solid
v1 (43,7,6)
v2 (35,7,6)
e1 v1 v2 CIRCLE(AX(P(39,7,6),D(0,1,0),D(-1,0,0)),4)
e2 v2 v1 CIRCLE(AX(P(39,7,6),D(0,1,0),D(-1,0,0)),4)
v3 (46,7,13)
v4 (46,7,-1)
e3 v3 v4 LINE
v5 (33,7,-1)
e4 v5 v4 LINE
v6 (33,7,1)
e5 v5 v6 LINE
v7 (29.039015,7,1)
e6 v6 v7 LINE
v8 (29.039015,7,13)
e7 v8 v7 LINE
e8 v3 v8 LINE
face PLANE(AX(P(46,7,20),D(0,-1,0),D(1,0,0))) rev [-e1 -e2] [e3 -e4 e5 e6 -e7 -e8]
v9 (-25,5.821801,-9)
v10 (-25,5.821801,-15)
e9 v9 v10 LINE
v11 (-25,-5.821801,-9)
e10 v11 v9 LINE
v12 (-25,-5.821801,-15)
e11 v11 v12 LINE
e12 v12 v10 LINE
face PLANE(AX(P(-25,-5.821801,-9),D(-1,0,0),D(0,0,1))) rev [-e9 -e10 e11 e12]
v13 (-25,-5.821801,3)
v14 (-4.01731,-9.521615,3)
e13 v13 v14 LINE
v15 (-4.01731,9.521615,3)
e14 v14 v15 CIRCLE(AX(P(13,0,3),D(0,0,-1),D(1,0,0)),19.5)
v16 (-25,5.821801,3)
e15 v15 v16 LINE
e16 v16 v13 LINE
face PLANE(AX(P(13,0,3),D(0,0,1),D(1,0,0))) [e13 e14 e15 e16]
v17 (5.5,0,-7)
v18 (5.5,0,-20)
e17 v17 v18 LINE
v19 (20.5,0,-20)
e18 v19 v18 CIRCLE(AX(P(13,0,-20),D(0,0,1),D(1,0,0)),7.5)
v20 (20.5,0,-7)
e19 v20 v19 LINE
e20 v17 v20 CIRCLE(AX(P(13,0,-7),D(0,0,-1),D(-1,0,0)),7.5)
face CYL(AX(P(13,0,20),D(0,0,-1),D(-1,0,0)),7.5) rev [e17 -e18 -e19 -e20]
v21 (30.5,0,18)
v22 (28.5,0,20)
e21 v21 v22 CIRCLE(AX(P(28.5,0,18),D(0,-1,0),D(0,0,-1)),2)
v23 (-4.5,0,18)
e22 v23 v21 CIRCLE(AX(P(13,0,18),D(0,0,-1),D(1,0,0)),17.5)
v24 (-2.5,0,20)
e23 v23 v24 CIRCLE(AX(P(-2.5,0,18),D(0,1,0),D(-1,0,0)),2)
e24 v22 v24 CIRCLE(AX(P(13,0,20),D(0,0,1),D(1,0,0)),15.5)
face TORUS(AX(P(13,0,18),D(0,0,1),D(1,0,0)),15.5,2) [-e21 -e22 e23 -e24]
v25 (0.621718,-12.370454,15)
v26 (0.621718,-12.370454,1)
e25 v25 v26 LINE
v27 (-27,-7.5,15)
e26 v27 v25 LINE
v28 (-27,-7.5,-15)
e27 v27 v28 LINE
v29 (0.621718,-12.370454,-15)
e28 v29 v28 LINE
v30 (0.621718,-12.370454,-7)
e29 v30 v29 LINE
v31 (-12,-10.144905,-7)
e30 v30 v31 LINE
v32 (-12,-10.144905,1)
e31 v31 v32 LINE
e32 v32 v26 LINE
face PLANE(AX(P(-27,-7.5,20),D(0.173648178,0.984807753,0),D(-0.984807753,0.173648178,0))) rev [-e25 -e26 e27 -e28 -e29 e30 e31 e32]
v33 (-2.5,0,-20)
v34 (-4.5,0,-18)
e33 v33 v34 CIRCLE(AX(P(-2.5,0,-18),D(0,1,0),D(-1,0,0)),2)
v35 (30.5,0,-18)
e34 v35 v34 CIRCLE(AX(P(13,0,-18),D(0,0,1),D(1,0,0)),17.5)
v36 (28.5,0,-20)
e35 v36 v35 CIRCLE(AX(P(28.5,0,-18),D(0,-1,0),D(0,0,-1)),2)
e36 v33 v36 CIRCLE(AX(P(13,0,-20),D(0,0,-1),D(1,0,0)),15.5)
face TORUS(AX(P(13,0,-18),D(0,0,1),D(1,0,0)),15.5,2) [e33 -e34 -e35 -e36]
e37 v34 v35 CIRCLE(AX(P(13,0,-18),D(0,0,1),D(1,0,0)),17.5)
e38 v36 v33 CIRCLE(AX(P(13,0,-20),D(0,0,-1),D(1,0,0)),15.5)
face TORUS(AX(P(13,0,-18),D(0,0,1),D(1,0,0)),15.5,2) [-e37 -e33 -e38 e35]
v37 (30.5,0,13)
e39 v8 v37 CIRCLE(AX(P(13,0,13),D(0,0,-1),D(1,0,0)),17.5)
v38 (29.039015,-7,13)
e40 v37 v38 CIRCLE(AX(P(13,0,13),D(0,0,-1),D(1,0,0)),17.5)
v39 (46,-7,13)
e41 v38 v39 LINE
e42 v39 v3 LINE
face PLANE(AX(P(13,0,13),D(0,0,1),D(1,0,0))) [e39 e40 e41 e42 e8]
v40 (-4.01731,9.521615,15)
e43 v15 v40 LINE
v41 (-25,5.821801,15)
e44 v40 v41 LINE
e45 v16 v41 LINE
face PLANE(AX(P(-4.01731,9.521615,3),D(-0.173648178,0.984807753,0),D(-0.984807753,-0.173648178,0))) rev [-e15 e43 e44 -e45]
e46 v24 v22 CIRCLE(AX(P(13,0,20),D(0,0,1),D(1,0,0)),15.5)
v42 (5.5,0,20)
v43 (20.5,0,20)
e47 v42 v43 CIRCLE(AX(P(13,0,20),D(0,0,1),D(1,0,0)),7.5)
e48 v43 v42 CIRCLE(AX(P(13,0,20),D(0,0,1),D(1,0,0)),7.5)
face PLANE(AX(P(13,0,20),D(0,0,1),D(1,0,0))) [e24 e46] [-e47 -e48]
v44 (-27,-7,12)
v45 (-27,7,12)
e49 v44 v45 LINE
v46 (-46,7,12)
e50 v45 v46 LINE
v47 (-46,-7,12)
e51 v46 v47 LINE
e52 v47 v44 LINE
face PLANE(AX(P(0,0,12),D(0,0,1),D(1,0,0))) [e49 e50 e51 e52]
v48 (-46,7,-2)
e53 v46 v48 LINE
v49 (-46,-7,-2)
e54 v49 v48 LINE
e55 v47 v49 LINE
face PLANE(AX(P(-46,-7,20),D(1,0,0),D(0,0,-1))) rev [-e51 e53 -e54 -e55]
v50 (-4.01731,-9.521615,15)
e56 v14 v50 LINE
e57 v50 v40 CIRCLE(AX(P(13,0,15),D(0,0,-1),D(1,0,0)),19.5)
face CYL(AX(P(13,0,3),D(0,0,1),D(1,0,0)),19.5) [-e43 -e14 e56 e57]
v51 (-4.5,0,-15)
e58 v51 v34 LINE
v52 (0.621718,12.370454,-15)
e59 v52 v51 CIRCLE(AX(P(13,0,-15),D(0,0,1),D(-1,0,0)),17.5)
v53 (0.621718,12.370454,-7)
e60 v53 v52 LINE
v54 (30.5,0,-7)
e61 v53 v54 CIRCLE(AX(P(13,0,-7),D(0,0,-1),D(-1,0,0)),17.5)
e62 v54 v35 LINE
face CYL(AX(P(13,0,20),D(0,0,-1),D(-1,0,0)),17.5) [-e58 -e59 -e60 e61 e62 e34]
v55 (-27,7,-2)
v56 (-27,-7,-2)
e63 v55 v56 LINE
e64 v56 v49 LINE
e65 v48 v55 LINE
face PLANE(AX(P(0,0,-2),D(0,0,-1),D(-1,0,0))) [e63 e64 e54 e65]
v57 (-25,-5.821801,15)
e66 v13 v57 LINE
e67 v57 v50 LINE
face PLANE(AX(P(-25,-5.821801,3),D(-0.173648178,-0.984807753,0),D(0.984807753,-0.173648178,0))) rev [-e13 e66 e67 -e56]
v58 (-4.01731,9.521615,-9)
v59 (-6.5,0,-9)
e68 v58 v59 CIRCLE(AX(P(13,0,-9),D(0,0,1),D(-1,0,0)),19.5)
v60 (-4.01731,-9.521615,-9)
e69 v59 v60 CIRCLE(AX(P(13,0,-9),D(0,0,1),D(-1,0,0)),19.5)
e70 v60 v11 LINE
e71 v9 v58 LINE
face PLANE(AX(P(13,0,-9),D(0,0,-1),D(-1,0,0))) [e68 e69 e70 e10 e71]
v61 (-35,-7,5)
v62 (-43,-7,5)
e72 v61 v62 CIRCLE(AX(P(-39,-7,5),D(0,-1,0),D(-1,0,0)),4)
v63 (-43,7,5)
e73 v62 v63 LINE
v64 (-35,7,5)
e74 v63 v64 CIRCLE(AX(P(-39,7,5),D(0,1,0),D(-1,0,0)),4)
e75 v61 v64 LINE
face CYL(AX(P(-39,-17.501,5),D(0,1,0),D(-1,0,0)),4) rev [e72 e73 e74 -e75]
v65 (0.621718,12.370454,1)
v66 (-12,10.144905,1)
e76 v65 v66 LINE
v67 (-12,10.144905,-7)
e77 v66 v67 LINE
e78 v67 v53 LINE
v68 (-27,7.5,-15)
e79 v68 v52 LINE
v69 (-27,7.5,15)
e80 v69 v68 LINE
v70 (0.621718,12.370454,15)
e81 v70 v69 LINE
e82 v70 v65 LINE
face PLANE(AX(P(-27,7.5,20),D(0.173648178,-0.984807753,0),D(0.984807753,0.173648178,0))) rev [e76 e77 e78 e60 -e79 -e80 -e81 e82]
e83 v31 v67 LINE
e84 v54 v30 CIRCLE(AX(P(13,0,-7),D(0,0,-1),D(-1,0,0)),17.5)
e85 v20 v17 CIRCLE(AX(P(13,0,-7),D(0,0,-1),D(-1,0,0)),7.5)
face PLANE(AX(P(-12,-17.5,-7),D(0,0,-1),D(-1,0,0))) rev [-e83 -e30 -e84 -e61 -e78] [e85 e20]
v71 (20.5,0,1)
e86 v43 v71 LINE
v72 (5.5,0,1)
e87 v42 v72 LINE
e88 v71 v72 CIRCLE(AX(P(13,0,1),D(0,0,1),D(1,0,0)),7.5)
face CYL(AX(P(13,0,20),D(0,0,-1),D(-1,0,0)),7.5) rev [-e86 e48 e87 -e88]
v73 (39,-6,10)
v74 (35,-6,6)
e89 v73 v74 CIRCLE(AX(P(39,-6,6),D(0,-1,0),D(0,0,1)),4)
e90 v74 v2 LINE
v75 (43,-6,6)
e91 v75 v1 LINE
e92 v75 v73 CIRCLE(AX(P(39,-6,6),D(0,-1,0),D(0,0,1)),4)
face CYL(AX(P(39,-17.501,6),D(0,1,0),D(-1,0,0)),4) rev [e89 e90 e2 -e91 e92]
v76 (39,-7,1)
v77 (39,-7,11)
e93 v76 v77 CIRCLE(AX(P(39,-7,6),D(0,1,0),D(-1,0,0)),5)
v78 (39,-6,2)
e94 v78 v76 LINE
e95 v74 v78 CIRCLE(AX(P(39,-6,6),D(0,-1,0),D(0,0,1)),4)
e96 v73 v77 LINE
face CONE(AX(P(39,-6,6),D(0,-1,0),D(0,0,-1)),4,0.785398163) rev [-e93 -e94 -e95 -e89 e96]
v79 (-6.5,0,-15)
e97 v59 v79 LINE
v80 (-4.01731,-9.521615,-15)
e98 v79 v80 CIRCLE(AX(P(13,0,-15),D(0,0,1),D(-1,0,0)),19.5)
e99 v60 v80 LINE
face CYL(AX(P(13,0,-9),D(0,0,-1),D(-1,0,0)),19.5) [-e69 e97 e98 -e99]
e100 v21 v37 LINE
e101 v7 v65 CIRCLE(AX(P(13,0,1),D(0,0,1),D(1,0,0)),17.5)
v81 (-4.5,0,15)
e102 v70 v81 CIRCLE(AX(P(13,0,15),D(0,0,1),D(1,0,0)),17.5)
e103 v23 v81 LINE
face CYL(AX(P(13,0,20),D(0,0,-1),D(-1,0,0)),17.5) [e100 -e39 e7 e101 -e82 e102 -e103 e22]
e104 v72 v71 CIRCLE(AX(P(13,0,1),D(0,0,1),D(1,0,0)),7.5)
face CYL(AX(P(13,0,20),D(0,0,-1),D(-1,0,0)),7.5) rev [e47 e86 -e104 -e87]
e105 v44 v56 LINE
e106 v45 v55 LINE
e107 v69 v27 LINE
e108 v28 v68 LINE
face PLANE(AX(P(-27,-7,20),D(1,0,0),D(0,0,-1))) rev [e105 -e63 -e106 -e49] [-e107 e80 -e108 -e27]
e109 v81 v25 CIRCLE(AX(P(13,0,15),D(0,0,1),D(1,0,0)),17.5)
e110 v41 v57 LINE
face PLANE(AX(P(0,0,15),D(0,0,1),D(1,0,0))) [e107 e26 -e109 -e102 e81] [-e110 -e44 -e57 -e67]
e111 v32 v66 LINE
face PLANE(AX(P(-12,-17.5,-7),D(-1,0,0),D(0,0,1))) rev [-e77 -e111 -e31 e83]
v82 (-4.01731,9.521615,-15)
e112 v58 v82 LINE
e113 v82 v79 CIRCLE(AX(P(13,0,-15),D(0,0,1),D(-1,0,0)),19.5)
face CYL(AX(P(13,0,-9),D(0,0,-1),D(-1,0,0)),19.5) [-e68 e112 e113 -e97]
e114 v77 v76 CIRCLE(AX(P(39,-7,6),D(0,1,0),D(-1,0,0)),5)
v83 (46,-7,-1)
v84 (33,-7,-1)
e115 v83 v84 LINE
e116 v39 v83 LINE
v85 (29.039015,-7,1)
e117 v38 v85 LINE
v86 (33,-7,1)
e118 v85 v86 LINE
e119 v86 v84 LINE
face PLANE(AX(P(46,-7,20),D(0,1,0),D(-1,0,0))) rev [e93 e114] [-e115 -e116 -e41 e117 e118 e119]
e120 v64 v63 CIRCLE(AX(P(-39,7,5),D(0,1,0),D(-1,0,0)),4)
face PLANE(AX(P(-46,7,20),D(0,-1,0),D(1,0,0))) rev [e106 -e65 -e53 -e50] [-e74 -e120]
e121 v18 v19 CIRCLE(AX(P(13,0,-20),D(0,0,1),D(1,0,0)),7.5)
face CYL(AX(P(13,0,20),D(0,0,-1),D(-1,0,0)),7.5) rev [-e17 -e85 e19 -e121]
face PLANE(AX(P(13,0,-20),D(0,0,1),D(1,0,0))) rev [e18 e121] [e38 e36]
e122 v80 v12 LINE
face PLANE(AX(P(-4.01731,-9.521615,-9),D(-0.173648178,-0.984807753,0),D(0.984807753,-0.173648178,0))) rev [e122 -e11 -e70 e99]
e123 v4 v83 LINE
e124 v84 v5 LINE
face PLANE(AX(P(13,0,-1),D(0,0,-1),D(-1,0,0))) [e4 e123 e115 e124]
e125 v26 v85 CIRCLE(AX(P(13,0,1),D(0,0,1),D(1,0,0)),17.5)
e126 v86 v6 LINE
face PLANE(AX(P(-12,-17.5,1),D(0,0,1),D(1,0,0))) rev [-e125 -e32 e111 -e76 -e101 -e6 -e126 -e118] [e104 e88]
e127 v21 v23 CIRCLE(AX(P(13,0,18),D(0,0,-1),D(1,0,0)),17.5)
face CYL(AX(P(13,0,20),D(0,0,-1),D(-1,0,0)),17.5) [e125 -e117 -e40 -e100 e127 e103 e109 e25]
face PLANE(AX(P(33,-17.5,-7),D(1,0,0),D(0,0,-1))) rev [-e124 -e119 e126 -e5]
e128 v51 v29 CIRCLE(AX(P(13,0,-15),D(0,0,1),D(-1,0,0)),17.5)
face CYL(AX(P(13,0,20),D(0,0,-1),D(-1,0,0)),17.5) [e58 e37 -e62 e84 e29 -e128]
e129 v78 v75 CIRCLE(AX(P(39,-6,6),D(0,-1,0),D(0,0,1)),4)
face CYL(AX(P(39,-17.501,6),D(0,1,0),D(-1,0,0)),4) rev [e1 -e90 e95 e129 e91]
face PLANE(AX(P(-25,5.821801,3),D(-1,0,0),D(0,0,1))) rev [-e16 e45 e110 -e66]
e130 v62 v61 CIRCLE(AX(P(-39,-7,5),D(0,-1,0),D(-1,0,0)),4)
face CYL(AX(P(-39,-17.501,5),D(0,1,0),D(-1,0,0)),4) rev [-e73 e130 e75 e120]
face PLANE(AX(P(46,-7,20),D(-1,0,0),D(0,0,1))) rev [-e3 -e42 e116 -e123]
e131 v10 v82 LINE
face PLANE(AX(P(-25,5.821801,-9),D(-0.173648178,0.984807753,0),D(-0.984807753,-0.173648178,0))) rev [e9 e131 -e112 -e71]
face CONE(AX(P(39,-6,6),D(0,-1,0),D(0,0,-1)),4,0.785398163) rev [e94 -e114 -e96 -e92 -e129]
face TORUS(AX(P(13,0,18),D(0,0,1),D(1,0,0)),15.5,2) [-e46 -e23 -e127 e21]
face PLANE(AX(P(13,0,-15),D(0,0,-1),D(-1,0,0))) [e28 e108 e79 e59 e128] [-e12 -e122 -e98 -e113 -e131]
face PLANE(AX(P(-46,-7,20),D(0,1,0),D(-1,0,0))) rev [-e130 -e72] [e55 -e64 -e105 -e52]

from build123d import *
from build123d.topology import SkipClean

# Parameters (mm, degrees)
BRACKET_SIDE_PROFILE_SKETCH_R = 7.5
BRACKET_BODY_40MM_DEPTH       = 20
TOP_SLOT_CUT_15X19_DEPTH      = 54.124852941
TOP_SLOT_CUT_15X19_DEPTH_BACK = 54.124852941
TOP_SLOT_SKETCH_W             = 45
TOP_SLOT_SKETCH_H             = 8
SIDE_RELIEF_A_CUT_7MM_DEPTH   = 7
SIDE_RELIEF_B_SKETCH_W        = 19
SIDE_RELIEF_B_SKETCH_H        = 14
SIDE_RELIEF_B_CUT_7MM_DEPTH   = 7
LUG_TRIM_A_CUT_5MM_DEPTH      = 5
LUG_START                     = -5
LUG_TRIM_B_CUT_5MM_DEPTH      = 5
HUB_GAP_SKETCH_W              = 19
HUB_GAP_SKETCH_H              = 14
HUB_GAP_CUT_18MM_DEPTH        = 18
RELIEF_STEP_SKETCH_W          = 19
RELIEF_STEP_SKETCH_H          = 14
RELIEF_STEP_CUT_1MM_DEPTH     = 1
WINDOW_START                  = -19
WINDOW_OPENING_CUT_19MM_DEPTH = 19
LUG_HOLE_A_CUT_12MM_DEPTH     = 12
LUG_START_2                   = -6
LUG_HOLE_B_CUT_6MM_DEPTH      = 6
EDGE_FILLET_R2_R              = 2
HUB_BORE_CUT_REACH            = 57.823
HUB_BORE_SKETCH_R             = 4
BORE_CHAMFER_1X45_SIZE        = 1


with BuildPart() as part:
    # Bracket Side Profile Sketch → Bracket Body 40mm (new, symmetric)
    with BuildSketch(Plane.XY):
        with BuildLine():
            Line((-46, -7), (-46, 7))
            Line((-46, 7), (-27, 7))
            Line((-27, 7), (-27, 7.5))
            Line((-27, 7.5), (0.62171804, 12.370454144))
            ThreePointArc((0.62171804, 12.370454144), (16.249720896, 17.195619038), (29.039014932, 7))
            Line((29.039014932, 7), (46, 7))
            Line((46, 7), (46, -7))
            Line((46, -7), (29.039014932, -7))
            ThreePointArc((29.039014932, -7), (16.249720896, -17.195619038), (0.62171804, -12.370454144))
            Line((0.62171804, -12.370454144), (-27, -7.5))
            Line((-27, -7.5), (-27, -7))
            Line((-27, -7), (-46, -7))
        make_face()
        with Locations((13, 0)):
            Circle(BRACKET_SIDE_PROFILE_SKETCH_R, mode=Mode.SUBTRACT)
    extrude(amount=BRACKET_BODY_40MM_DEPTH, both=True)

    # Top Slot Sketch → Top Slot Cut 15x19 (cut, two sides: drawn at the far end of the back side and taken through both)
    with BuildSketch(Plane(origin=(0, 0, 0), x_dir=(1, 0, 0), z_dir=(0, 1, 0)).offset(-TOP_SLOT_CUT_15X19_DEPTH_BACK)):
        with Locations((10.5, 3)):
            Rectangle(TOP_SLOT_SKETCH_W, TOP_SLOT_SKETCH_H)
    extrude(amount=TOP_SLOT_CUT_15X19_DEPTH + TOP_SLOT_CUT_15X19_DEPTH_BACK, mode=Mode.SUBTRACT)

    # Side Relief A Sketch → Side Relief A Cut 7mm (cut)
    with BuildSketch(Plane.XY.offset(20)):
        with BuildLine():
            Line((29.039014932, -7), (46, -7))
            Line((46, -7), (46, 7))
            Line((46, 7), (29.039014932, 7))
            ThreePointArc((29.039014932, 7), (30.5, 0), (29.039014932, -7))
        make_face()
    extrude(amount=-SIDE_RELIEF_A_CUT_7MM_DEPTH, mode=Mode.SUBTRACT)

    # Side Relief B Sketch → Side Relief B Cut 7mm (cut)
    with BuildSketch(Plane.XY.offset(20)):
        with Locations((-36.5, 0)):
            Rectangle(SIDE_RELIEF_B_SKETCH_W, SIDE_RELIEF_B_SKETCH_H)
    extrude(amount=-SIDE_RELIEF_B_CUT_7MM_DEPTH, mode=Mode.SUBTRACT)

    # Lug Trim A Sketch → Lug Trim A Cut 5mm (cut)
    with SkipClean():  # the faces are left unmerged after this step: merging them gives an invalid solid
        with BuildSketch(Plane.XY.offset(20)):
            with BuildLine():
                ThreePointArc((0.62171804, 12.370454144), (-4.5, 0), (0.62171804, -12.370454144))
                Line((0.62171804, -12.370454144), (-27, -7.5))
                Line((-27, -7.5), (-27, 7.5))
                Line((-27, 7.5), (0.62171804, 12.370454144))
            make_face()
        extrude(amount=-LUG_TRIM_A_CUT_5MM_DEPTH, mode=Mode.SUBTRACT)

    # Lug Trim B Sketch → Lug Trim B Cut 5mm (cut)
    with SkipClean():  # the faces are left unmerged after this step: merging them gives an invalid solid
        with BuildSketch(Plane(origin=(0, 0, -20), x_dir=(-1, 0, 0), z_dir=(0, 0, -1)).offset(LUG_START)):
            with BuildLine():
                Line((27, -7.5), (-0.62171804, -12.370454144))
                ThreePointArc((-0.62171804, -12.370454144), (4.5, 0), (-0.62171804, 12.370454144))
                Line((-0.62171804, 12.370454144), (27, 7.5))
                Line((27, 7.5), (27, -7.5))
            make_face()
        extrude(amount=LUG_TRIM_B_CUT_5MM_DEPTH, mode=Mode.SUBTRACT)

    # Hub Gap Sketch → Hub Gap Cut 18mm (cut)
    with SkipClean():  # the faces are left unmerged after this step: merging them gives an invalid solid
        with BuildSketch(Plane(origin=(0, 0, -20), x_dir=(-1, 0, 0), z_dir=(0, 0, -1))):
            with Locations((36.5, 0)):
                Rectangle(HUB_GAP_SKETCH_W, HUB_GAP_SKETCH_H)
        extrude(amount=-HUB_GAP_CUT_18MM_DEPTH, mode=Mode.SUBTRACT)

    # Relief Step Sketch → Relief Step Cut 1mm (cut)
    with SkipClean():  # the faces are left unmerged after this step: merging them gives an invalid solid
        with BuildSketch(Plane.XY.offset(13)):
            with Locations((-36.5, 0)):
                Rectangle(RELIEF_STEP_SKETCH_W, RELIEF_STEP_SKETCH_H)
        extrude(amount=-RELIEF_STEP_CUT_1MM_DEPTH, mode=Mode.SUBTRACT)

    # Window Opening Sketch → Window Opening Cut 19mm (cut)
    with SkipClean():  # the faces are left unmerged after this step: merging them gives an invalid solid
        with BuildSketch(Plane(origin=(0, 0, -20), x_dir=(-1, 0, 0), z_dir=(0, 0, -1)).offset(WINDOW_START)):
            with BuildLine():
                Line((-29.039014932, 7), (-46, 7))
                Line((-46, 7), (-46, -7))
                Line((-46, -7), (-29.039014932, -7))
                ThreePointArc((-29.039014932, -7), (-30.5, 0), (-29.039014932, 7))
            make_face()
        extrude(amount=WINDOW_OPENING_CUT_19MM_DEPTH, mode=Mode.SUBTRACT)

    # Lug Hole A Sketch → Lug Hole A Cut 12mm (cut)
    with SkipClean():  # the faces are left unmerged after this step: merging them gives an invalid solid
        with BuildSketch(Plane.XY.offset(15)):
            with BuildLine():
                Line((-4.017310196, 9.521615078), (-25, 5.821800738))
                Line((-25, 5.821800738), (-25, -5.821800738))
                Line((-25, -5.821800738), (-4.017310196, -9.521615078))
                ThreePointArc((-4.017310196, -9.521615078), (-6.5, 0), (-4.017310196, 9.521615078))
            make_face()
        extrude(amount=-LUG_HOLE_A_CUT_12MM_DEPTH, mode=Mode.SUBTRACT)

    # Lug Hole B Sketch → Lug Hole B Cut 6mm (cut)
    with SkipClean():  # the faces are left unmerged after this step: merging them gives an invalid solid
        with BuildSketch(Plane(origin=(0, 0, -15), x_dir=(-1, 0, 0), z_dir=(0, 0, -1)).offset(LUG_START_2)):
            with BuildLine():
                Line((4.017310196, -9.521615078), (25, -5.821800738))
                Line((25, -5.821800738), (25, 5.821800738))
                Line((25, 5.821800738), (4.017310196, 9.521615078))
                ThreePointArc((4.017310196, 9.521615078), (6.5, 0), (4.017310196, -9.521615078))
            make_face()
        extrude(amount=LUG_HOLE_B_CUT_6MM_DEPTH, mode=Mode.SUBTRACT)

    # Edge Fillet R2
    edge_fillet_r2_edges = [part.edges().sort_by_distance(p)[0] for p in [
        (30.5, 0, -20),
        (30.5, 0, 20),
    ]]
    fillet(edge_fillet_r2_edges, radius=EDGE_FILLET_R2_R)

    # Hub Bore Sketch → Hub Bore Cut (cut, up to next)
    with BuildSketch(Plane(origin=(0, 7, 0), x_dir=(1, 0, 0), z_dir=(0, 1, 0)), mode=Mode.PRIVATE) as hub_bore_cut_sk1:
        with Locations(Location((-39, -5, 0), (0, 0, 180))):
            Circle(HUB_BORE_SKETCH_R)
    hub_bore_cut_tool1 = extrude(hub_bore_cut_sk1.sketch, amount=-HUB_BORE_CUT_REACH, mode=Mode.PRIVATE) & part.part
    # Hub Bore Sketch → Hub Bore Cut (cut, up to next)
    with BuildSketch(Plane(origin=(0, 7, 0), x_dir=(1, 0, 0), z_dir=(0, 1, 0)), mode=Mode.PRIVATE) as hub_bore_cut_sk2:
        with Locations(Location((39, -6, 0), (0, 0, 180))):
            Circle(HUB_BORE_SKETCH_R)
    hub_bore_cut_tool2 = extrude(hub_bore_cut_sk2.sketch, amount=-HUB_BORE_CUT_REACH, mode=Mode.PRIVATE) & part.part
    add(hub_bore_cut_tool1.solids().sort_by_distance((-39, 7, 5))[0], mode=Mode.SUBTRACT)
    add(hub_bore_cut_tool2.solids().sort_by_distance((39, 7, 6))[0], mode=Mode.SUBTRACT)

    # Bore Chamfer 1x45
    bore_chamfer_1x45_edges = [part.edges().sort_by_distance(p)[0] for p in [
        (43, -7, 6),
    ]]
    chamfer(bore_chamfer_1x45_edges, length=BORE_CHAMFER_1X45_SIZE)


solid = part.part
